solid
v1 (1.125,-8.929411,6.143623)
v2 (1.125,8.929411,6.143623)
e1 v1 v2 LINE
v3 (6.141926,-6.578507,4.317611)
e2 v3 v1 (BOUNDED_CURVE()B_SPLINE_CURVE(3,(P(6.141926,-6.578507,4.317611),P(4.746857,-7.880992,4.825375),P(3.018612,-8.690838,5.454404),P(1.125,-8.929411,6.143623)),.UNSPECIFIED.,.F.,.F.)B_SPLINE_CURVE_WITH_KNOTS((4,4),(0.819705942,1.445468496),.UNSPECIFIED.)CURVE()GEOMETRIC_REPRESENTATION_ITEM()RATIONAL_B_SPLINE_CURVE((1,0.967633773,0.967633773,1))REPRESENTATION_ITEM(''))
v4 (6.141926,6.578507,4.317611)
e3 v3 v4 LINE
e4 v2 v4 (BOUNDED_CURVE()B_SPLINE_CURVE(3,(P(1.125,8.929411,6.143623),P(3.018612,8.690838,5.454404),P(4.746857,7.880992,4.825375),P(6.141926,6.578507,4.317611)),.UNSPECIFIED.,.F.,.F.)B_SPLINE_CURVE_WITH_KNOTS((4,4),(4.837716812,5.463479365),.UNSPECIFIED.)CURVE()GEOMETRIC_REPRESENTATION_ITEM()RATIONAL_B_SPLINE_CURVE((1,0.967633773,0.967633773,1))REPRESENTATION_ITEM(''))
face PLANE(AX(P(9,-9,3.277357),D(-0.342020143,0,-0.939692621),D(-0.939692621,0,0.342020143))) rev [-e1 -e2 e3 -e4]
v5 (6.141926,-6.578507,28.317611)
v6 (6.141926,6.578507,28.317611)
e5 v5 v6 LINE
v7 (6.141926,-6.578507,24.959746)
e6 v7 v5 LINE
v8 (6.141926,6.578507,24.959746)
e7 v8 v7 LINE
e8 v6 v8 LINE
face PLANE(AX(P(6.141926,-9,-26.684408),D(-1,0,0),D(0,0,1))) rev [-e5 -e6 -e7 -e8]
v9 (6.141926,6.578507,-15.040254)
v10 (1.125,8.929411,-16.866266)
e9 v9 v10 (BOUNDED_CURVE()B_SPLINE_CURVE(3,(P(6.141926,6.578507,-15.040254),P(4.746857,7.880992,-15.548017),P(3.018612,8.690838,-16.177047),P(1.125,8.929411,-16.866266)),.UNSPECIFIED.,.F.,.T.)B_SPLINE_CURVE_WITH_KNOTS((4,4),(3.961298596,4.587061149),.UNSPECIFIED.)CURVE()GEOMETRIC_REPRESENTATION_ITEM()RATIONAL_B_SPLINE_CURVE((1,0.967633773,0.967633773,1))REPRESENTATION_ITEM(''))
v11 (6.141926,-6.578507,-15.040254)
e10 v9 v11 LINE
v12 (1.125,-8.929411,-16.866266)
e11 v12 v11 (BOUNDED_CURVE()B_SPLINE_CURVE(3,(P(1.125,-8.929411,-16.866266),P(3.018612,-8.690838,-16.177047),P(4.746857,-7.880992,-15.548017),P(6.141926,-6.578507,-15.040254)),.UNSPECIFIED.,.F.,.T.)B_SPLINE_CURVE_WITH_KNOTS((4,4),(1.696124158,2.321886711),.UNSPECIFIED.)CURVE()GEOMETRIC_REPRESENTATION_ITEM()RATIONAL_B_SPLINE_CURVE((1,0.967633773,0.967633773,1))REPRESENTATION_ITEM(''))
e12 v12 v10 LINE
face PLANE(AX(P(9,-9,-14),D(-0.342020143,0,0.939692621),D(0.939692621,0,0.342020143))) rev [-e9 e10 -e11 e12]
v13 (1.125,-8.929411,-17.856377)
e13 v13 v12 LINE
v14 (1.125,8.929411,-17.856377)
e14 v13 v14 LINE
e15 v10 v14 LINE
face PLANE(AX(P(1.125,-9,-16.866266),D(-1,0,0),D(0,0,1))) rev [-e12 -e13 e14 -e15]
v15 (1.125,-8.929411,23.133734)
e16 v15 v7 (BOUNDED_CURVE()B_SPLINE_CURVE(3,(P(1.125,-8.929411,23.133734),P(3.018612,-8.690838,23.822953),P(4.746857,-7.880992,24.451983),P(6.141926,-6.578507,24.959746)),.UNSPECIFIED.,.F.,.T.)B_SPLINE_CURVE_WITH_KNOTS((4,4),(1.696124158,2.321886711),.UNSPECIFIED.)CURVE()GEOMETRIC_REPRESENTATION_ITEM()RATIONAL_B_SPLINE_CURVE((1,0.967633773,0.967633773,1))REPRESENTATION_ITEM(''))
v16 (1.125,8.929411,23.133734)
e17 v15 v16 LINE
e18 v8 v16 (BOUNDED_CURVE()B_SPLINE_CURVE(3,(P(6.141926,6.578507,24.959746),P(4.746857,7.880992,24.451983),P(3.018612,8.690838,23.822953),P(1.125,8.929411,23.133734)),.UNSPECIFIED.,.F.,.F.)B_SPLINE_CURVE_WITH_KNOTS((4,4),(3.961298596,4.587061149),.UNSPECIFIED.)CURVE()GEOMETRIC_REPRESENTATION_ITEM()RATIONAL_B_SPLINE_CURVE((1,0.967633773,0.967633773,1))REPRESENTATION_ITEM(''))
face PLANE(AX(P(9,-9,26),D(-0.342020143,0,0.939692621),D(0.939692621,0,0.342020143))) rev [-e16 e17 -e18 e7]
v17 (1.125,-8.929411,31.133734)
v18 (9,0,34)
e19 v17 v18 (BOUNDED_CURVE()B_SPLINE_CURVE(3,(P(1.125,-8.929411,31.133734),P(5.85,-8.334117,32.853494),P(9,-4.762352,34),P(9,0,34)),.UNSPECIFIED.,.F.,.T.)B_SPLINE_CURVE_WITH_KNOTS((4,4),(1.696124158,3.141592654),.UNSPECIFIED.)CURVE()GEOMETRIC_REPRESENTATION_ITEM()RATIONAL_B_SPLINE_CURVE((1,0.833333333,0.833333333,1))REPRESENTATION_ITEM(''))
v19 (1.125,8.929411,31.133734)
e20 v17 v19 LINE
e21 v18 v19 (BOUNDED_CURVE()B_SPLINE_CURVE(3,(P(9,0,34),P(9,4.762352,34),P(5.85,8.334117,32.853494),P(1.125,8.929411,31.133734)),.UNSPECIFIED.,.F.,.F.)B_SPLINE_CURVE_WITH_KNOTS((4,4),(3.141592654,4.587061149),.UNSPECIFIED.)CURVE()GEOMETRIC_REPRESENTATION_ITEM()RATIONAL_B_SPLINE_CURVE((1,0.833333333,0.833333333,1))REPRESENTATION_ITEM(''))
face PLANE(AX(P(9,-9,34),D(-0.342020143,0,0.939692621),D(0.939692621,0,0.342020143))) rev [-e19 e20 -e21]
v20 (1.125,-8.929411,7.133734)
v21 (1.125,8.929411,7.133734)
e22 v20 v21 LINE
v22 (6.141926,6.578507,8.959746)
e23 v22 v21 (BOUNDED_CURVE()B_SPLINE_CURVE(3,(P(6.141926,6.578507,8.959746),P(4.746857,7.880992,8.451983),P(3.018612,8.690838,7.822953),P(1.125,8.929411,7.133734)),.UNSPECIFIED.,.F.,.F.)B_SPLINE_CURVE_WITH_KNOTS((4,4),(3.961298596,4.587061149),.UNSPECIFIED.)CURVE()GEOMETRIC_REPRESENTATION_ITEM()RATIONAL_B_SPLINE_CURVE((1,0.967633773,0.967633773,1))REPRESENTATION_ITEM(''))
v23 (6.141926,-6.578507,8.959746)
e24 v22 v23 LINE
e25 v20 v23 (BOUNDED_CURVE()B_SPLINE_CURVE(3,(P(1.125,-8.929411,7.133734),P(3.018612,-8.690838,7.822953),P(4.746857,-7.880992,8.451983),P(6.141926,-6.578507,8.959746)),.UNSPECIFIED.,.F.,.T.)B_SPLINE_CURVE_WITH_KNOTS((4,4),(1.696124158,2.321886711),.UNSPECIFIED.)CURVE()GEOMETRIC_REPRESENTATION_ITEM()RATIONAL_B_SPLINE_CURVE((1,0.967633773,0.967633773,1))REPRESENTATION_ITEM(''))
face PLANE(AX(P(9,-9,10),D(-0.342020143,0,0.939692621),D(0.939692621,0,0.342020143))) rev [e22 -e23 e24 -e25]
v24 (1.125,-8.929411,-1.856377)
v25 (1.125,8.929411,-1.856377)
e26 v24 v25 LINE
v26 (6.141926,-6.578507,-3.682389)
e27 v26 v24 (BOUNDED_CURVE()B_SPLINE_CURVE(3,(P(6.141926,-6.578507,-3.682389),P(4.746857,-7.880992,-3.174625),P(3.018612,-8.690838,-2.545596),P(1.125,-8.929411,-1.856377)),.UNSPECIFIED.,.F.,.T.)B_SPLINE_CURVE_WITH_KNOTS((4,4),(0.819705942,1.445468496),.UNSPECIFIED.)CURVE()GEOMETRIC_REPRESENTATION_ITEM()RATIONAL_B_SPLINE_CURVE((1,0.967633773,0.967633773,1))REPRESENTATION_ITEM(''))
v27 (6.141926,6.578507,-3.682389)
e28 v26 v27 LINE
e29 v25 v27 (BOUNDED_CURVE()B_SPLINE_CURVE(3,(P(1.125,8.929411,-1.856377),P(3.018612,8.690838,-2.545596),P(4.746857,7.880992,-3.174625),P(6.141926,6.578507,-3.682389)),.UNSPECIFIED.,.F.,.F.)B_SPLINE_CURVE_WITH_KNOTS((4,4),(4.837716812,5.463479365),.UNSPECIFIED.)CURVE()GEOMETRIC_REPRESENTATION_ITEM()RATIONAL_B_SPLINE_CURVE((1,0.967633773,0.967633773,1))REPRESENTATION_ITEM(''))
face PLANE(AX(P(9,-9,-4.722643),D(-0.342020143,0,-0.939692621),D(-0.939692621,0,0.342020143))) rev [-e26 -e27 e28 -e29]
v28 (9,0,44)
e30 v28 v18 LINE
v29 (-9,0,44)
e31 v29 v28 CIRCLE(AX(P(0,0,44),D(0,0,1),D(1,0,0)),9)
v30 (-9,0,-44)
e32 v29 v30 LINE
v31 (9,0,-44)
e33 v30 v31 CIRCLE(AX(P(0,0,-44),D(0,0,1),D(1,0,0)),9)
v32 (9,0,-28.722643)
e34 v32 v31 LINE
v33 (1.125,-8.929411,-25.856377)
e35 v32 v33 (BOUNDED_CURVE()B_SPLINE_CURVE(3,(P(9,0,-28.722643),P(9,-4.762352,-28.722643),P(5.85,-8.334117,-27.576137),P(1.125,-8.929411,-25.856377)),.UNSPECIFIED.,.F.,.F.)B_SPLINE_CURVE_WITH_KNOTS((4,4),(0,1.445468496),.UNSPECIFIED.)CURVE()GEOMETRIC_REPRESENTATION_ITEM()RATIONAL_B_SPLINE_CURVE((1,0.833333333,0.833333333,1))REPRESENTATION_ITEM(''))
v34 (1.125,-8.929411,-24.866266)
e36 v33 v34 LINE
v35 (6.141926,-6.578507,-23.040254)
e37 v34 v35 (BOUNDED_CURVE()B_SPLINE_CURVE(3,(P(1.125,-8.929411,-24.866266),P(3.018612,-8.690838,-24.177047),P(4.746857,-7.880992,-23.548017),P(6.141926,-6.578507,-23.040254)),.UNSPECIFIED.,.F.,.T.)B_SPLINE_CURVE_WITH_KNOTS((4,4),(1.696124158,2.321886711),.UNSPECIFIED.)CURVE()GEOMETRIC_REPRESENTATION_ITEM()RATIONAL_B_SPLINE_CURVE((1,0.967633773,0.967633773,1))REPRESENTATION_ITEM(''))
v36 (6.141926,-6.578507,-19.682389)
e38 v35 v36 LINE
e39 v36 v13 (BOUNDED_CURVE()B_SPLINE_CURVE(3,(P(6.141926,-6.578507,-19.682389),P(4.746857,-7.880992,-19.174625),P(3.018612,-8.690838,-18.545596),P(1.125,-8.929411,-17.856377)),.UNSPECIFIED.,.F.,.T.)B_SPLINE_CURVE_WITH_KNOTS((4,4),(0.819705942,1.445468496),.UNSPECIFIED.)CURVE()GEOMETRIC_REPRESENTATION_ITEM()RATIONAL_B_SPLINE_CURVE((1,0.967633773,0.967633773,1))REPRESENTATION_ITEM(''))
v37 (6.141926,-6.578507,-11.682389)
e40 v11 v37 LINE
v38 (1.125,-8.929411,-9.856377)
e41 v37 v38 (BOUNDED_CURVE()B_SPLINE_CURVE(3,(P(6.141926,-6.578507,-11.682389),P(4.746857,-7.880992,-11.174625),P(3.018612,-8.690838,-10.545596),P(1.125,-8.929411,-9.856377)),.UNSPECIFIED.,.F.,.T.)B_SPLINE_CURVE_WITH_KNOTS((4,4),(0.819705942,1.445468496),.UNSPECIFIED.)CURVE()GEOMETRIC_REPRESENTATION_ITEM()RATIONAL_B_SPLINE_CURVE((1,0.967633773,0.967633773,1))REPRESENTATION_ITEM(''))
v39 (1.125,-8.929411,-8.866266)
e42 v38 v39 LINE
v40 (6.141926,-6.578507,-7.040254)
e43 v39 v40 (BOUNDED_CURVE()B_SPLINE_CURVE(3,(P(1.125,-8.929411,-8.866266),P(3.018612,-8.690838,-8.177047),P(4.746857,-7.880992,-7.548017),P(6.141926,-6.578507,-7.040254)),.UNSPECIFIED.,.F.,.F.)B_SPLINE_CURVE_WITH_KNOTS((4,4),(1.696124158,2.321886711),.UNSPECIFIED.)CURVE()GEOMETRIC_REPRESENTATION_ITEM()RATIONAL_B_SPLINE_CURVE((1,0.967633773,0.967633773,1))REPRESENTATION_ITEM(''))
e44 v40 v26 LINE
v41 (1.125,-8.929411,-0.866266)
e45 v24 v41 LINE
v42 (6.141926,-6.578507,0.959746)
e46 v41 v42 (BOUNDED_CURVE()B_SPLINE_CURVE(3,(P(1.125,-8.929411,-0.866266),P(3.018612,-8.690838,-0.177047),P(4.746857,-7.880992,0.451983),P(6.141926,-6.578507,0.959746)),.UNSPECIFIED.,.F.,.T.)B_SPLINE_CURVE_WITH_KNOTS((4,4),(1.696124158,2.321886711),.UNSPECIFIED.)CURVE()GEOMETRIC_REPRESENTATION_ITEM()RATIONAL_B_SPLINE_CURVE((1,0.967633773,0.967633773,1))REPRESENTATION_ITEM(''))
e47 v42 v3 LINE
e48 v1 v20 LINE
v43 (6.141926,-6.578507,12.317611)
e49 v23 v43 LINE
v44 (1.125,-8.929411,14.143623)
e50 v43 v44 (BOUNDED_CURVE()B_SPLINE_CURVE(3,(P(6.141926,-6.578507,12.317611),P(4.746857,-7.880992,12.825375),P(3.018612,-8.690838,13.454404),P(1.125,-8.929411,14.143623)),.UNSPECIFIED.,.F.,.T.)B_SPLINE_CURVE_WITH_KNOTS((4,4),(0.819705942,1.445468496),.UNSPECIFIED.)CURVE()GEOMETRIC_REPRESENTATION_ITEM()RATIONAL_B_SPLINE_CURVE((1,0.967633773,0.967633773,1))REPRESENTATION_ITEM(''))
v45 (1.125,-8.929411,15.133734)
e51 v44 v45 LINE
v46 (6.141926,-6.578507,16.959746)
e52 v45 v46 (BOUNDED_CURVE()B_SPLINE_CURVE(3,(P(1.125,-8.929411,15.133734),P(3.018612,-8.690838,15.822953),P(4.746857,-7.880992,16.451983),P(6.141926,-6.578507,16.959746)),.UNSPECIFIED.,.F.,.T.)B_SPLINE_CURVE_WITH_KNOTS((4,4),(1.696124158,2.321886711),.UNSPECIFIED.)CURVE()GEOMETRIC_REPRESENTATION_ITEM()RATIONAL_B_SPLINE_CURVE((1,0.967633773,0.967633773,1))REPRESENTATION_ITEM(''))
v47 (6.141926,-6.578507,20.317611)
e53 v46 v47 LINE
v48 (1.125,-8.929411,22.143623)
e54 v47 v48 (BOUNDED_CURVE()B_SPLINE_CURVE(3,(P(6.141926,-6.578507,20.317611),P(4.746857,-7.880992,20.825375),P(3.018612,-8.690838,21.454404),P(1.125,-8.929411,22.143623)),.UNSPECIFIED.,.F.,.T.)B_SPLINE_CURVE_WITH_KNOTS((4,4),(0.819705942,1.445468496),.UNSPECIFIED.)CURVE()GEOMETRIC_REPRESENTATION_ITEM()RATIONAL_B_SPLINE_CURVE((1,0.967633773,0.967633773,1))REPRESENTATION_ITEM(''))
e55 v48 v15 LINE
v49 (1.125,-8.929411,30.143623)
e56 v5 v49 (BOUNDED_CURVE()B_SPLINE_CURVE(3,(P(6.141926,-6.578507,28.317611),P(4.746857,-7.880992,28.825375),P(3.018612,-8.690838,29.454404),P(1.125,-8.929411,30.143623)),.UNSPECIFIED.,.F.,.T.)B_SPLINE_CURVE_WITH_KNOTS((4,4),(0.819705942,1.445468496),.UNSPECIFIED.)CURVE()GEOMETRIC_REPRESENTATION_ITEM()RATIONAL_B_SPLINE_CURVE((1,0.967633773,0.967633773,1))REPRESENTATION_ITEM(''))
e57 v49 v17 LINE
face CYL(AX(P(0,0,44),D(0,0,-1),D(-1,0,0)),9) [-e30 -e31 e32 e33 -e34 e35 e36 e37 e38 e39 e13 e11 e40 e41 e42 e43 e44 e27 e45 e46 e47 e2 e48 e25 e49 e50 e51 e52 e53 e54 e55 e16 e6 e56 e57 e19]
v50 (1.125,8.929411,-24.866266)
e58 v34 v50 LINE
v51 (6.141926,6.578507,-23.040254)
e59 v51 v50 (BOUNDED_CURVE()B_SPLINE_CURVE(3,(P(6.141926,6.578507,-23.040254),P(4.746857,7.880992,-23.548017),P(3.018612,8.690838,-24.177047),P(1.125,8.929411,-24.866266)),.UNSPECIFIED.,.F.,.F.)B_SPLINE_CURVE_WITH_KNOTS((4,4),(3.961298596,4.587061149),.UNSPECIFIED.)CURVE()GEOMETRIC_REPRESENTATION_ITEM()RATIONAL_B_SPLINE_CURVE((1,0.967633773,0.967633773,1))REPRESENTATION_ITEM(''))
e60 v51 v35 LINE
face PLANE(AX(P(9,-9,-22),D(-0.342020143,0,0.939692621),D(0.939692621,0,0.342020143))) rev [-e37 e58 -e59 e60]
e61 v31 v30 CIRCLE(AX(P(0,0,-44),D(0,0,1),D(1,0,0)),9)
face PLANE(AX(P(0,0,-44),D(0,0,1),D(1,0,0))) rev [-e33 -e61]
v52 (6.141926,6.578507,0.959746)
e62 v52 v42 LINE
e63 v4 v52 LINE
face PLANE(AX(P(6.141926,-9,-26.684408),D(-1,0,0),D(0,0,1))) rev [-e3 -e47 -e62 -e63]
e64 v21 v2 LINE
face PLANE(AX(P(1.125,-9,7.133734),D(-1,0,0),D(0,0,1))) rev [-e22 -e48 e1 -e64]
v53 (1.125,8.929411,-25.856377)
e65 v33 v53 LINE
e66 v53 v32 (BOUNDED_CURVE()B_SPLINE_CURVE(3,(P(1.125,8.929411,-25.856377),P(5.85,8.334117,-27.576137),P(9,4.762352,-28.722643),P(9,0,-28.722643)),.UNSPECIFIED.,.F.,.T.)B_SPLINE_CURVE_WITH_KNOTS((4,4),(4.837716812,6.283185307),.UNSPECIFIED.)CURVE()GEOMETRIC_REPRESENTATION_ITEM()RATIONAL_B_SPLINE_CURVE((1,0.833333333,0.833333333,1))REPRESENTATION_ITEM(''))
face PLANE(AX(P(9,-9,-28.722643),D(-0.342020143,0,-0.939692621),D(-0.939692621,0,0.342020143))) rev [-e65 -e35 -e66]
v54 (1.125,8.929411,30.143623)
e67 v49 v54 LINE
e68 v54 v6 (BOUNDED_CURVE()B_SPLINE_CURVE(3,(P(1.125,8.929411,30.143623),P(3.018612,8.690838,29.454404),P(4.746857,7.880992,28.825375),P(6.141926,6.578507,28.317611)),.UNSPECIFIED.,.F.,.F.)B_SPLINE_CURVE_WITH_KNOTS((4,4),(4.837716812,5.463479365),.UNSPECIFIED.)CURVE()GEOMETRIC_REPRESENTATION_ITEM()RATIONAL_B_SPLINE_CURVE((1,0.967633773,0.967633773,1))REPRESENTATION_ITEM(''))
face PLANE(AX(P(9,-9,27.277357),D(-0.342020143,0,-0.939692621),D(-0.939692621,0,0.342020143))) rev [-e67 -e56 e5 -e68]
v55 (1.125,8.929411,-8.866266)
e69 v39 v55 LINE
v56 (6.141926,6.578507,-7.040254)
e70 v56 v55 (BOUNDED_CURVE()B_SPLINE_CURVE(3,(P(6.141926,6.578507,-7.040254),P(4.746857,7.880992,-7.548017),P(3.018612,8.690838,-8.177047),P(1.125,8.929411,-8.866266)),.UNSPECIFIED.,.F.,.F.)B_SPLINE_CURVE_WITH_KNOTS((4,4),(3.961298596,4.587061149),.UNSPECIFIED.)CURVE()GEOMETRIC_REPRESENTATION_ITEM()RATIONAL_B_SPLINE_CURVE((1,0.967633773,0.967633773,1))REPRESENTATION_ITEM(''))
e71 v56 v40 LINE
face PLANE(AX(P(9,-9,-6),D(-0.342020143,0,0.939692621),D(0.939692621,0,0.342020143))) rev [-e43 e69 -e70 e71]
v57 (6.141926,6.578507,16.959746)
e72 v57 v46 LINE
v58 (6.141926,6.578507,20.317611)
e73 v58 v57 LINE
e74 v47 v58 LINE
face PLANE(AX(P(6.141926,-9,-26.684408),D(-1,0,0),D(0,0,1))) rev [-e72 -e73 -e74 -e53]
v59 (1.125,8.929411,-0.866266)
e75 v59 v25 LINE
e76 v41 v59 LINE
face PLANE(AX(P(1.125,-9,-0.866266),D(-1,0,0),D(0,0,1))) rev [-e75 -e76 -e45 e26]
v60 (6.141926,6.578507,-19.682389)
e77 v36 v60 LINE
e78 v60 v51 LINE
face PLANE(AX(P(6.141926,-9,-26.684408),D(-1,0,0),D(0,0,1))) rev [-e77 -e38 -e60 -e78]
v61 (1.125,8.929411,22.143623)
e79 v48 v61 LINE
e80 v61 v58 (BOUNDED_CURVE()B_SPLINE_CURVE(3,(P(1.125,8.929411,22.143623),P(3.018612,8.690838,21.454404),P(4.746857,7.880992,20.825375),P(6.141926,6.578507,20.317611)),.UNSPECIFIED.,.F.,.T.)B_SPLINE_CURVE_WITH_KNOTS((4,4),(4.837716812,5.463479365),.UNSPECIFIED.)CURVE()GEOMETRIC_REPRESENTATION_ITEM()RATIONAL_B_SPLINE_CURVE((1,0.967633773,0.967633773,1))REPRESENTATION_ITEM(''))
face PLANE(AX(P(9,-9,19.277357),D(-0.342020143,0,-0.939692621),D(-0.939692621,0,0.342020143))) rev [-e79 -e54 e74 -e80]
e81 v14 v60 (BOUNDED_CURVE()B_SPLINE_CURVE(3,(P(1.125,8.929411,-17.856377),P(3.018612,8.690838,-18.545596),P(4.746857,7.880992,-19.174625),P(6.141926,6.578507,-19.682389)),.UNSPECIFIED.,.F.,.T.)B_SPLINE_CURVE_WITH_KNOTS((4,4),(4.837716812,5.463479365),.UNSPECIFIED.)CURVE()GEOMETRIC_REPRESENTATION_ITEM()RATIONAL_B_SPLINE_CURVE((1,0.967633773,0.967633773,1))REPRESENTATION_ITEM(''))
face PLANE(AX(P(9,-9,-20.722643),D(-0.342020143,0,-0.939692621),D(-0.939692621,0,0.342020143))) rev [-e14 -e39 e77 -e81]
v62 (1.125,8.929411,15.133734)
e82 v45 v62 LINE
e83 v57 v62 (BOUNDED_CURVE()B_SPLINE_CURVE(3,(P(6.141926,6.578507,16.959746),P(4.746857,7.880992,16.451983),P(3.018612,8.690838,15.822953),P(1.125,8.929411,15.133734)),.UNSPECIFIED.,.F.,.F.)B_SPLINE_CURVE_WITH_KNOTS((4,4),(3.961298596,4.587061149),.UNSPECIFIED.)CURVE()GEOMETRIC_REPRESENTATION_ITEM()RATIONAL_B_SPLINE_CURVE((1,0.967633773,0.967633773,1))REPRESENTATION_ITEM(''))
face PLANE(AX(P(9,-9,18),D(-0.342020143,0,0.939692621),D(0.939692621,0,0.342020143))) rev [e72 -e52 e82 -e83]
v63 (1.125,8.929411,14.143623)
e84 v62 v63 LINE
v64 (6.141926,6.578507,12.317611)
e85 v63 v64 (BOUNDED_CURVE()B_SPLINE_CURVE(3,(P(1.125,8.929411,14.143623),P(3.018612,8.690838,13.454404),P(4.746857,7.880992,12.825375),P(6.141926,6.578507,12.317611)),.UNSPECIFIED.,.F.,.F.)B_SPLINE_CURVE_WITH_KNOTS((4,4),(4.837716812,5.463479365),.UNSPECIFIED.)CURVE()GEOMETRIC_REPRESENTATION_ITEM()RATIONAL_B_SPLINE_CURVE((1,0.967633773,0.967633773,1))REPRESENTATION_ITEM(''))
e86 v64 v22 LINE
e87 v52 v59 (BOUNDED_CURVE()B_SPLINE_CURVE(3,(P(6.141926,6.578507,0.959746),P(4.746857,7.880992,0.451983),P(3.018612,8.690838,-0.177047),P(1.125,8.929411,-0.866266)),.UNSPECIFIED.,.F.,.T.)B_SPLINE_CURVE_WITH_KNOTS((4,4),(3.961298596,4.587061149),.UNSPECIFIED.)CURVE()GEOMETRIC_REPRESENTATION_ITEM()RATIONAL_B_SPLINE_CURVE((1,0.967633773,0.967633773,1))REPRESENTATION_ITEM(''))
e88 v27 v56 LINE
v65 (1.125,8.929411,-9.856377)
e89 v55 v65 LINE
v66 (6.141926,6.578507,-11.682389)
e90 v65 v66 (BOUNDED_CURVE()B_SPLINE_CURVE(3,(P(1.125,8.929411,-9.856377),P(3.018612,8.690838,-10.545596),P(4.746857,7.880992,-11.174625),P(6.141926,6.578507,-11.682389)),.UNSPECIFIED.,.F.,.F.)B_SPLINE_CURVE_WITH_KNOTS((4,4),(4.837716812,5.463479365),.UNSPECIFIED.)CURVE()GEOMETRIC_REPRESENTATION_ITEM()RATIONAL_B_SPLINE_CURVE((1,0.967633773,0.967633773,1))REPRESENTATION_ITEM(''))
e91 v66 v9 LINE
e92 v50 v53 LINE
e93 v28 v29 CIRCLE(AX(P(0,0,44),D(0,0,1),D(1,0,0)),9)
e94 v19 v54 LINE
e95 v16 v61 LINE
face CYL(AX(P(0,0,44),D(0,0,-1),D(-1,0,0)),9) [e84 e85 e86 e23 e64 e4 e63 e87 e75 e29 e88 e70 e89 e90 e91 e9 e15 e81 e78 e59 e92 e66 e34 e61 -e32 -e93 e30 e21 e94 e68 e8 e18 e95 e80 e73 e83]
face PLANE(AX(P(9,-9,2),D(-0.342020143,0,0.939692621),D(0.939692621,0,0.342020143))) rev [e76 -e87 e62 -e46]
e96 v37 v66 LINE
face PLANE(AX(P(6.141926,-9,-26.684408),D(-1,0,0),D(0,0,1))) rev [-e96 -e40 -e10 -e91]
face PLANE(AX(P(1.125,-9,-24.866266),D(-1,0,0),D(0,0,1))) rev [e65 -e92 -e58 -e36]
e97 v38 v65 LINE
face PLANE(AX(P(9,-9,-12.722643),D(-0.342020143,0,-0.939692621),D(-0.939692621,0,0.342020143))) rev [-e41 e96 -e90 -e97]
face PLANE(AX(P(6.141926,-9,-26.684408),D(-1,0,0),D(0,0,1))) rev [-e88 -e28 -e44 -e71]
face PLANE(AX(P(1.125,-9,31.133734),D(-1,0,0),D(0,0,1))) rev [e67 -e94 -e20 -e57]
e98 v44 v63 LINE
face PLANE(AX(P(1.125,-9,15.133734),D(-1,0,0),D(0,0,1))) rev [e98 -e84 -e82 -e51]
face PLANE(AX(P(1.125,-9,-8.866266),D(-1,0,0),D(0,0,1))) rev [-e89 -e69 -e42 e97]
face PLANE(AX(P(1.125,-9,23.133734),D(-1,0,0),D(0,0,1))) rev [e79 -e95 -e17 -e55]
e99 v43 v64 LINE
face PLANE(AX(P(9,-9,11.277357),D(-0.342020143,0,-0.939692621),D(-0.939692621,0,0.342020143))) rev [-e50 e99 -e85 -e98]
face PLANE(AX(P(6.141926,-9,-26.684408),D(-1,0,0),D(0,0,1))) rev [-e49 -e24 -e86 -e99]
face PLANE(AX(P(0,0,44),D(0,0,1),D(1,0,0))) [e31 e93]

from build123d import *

# Parameters (mm, degrees)
SKETCH1_R               = 9
BOSS_EXTRUDE1_DEPTH     = 44
CUT_EXTRUDE1_DEPTH      = 46.803929962
LPATTERN1_COUNT         = 8
LPATTERN1_PITCH         = 8
CUT_EXTRUDE2_DEPTH      = 46.803929962
CUT_EXTRUDE2_DEPTH_BACK = 46.803929962
SKETCH4_W               = 11.104020724
SKETCH4_H               = 55.76293723


with BuildPart() as part:
    # Sketch1 → Boss-Extrude1 (new, symmetric)
    with BuildSketch(Plane.XY):
        Circle(SKETCH1_R)
    extrude(amount=BOSS_EXTRUDE1_DEPTH, both=True)

    # Sketch2 → Cut-Extrude1 (cut, symmetric)
    with BuildSketch(Plane(origin=(0, 0, 0), x_dir=(1, 0, 0), z_dir=(0, 1, 0))):
        Polygon((9, -34), (1.125, -31.133734405), (1.125, -30.143622784), (9, -27.277357189), align=None)
    cut_extrude1 = extrude(amount=CUT_EXTRUDE1_DEPTH, both=True, mode=Mode.SUBTRACT)

    # LPattern1: Cut-Extrude1 ×8
    with Locations(*[(0, 0, -i * LPATTERN1_PITCH) for i in range(1, LPATTERN1_COUNT)]):
        add(cut_extrude1, mode=Mode.SUBTRACT)

    # Sketch4 → Cut-Extrude2 (cut, two sides: drawn at the far end of the back side and taken through both)
    with BuildSketch(Plane(origin=(0, 0, 0), x_dir=(1, 0, 0), z_dir=(0, 1, 0)).offset(-CUT_EXTRUDE2_DEPTH_BACK)):
        with Locations((11.693935952, -1.197060718)):
            Rectangle(SKETCH4_W, SKETCH4_H)
    extrude(amount=CUT_EXTRUDE2_DEPTH + CUT_EXTRUDE2_DEPTH_BACK, mode=Mode.SUBTRACT)


solid = part.part
